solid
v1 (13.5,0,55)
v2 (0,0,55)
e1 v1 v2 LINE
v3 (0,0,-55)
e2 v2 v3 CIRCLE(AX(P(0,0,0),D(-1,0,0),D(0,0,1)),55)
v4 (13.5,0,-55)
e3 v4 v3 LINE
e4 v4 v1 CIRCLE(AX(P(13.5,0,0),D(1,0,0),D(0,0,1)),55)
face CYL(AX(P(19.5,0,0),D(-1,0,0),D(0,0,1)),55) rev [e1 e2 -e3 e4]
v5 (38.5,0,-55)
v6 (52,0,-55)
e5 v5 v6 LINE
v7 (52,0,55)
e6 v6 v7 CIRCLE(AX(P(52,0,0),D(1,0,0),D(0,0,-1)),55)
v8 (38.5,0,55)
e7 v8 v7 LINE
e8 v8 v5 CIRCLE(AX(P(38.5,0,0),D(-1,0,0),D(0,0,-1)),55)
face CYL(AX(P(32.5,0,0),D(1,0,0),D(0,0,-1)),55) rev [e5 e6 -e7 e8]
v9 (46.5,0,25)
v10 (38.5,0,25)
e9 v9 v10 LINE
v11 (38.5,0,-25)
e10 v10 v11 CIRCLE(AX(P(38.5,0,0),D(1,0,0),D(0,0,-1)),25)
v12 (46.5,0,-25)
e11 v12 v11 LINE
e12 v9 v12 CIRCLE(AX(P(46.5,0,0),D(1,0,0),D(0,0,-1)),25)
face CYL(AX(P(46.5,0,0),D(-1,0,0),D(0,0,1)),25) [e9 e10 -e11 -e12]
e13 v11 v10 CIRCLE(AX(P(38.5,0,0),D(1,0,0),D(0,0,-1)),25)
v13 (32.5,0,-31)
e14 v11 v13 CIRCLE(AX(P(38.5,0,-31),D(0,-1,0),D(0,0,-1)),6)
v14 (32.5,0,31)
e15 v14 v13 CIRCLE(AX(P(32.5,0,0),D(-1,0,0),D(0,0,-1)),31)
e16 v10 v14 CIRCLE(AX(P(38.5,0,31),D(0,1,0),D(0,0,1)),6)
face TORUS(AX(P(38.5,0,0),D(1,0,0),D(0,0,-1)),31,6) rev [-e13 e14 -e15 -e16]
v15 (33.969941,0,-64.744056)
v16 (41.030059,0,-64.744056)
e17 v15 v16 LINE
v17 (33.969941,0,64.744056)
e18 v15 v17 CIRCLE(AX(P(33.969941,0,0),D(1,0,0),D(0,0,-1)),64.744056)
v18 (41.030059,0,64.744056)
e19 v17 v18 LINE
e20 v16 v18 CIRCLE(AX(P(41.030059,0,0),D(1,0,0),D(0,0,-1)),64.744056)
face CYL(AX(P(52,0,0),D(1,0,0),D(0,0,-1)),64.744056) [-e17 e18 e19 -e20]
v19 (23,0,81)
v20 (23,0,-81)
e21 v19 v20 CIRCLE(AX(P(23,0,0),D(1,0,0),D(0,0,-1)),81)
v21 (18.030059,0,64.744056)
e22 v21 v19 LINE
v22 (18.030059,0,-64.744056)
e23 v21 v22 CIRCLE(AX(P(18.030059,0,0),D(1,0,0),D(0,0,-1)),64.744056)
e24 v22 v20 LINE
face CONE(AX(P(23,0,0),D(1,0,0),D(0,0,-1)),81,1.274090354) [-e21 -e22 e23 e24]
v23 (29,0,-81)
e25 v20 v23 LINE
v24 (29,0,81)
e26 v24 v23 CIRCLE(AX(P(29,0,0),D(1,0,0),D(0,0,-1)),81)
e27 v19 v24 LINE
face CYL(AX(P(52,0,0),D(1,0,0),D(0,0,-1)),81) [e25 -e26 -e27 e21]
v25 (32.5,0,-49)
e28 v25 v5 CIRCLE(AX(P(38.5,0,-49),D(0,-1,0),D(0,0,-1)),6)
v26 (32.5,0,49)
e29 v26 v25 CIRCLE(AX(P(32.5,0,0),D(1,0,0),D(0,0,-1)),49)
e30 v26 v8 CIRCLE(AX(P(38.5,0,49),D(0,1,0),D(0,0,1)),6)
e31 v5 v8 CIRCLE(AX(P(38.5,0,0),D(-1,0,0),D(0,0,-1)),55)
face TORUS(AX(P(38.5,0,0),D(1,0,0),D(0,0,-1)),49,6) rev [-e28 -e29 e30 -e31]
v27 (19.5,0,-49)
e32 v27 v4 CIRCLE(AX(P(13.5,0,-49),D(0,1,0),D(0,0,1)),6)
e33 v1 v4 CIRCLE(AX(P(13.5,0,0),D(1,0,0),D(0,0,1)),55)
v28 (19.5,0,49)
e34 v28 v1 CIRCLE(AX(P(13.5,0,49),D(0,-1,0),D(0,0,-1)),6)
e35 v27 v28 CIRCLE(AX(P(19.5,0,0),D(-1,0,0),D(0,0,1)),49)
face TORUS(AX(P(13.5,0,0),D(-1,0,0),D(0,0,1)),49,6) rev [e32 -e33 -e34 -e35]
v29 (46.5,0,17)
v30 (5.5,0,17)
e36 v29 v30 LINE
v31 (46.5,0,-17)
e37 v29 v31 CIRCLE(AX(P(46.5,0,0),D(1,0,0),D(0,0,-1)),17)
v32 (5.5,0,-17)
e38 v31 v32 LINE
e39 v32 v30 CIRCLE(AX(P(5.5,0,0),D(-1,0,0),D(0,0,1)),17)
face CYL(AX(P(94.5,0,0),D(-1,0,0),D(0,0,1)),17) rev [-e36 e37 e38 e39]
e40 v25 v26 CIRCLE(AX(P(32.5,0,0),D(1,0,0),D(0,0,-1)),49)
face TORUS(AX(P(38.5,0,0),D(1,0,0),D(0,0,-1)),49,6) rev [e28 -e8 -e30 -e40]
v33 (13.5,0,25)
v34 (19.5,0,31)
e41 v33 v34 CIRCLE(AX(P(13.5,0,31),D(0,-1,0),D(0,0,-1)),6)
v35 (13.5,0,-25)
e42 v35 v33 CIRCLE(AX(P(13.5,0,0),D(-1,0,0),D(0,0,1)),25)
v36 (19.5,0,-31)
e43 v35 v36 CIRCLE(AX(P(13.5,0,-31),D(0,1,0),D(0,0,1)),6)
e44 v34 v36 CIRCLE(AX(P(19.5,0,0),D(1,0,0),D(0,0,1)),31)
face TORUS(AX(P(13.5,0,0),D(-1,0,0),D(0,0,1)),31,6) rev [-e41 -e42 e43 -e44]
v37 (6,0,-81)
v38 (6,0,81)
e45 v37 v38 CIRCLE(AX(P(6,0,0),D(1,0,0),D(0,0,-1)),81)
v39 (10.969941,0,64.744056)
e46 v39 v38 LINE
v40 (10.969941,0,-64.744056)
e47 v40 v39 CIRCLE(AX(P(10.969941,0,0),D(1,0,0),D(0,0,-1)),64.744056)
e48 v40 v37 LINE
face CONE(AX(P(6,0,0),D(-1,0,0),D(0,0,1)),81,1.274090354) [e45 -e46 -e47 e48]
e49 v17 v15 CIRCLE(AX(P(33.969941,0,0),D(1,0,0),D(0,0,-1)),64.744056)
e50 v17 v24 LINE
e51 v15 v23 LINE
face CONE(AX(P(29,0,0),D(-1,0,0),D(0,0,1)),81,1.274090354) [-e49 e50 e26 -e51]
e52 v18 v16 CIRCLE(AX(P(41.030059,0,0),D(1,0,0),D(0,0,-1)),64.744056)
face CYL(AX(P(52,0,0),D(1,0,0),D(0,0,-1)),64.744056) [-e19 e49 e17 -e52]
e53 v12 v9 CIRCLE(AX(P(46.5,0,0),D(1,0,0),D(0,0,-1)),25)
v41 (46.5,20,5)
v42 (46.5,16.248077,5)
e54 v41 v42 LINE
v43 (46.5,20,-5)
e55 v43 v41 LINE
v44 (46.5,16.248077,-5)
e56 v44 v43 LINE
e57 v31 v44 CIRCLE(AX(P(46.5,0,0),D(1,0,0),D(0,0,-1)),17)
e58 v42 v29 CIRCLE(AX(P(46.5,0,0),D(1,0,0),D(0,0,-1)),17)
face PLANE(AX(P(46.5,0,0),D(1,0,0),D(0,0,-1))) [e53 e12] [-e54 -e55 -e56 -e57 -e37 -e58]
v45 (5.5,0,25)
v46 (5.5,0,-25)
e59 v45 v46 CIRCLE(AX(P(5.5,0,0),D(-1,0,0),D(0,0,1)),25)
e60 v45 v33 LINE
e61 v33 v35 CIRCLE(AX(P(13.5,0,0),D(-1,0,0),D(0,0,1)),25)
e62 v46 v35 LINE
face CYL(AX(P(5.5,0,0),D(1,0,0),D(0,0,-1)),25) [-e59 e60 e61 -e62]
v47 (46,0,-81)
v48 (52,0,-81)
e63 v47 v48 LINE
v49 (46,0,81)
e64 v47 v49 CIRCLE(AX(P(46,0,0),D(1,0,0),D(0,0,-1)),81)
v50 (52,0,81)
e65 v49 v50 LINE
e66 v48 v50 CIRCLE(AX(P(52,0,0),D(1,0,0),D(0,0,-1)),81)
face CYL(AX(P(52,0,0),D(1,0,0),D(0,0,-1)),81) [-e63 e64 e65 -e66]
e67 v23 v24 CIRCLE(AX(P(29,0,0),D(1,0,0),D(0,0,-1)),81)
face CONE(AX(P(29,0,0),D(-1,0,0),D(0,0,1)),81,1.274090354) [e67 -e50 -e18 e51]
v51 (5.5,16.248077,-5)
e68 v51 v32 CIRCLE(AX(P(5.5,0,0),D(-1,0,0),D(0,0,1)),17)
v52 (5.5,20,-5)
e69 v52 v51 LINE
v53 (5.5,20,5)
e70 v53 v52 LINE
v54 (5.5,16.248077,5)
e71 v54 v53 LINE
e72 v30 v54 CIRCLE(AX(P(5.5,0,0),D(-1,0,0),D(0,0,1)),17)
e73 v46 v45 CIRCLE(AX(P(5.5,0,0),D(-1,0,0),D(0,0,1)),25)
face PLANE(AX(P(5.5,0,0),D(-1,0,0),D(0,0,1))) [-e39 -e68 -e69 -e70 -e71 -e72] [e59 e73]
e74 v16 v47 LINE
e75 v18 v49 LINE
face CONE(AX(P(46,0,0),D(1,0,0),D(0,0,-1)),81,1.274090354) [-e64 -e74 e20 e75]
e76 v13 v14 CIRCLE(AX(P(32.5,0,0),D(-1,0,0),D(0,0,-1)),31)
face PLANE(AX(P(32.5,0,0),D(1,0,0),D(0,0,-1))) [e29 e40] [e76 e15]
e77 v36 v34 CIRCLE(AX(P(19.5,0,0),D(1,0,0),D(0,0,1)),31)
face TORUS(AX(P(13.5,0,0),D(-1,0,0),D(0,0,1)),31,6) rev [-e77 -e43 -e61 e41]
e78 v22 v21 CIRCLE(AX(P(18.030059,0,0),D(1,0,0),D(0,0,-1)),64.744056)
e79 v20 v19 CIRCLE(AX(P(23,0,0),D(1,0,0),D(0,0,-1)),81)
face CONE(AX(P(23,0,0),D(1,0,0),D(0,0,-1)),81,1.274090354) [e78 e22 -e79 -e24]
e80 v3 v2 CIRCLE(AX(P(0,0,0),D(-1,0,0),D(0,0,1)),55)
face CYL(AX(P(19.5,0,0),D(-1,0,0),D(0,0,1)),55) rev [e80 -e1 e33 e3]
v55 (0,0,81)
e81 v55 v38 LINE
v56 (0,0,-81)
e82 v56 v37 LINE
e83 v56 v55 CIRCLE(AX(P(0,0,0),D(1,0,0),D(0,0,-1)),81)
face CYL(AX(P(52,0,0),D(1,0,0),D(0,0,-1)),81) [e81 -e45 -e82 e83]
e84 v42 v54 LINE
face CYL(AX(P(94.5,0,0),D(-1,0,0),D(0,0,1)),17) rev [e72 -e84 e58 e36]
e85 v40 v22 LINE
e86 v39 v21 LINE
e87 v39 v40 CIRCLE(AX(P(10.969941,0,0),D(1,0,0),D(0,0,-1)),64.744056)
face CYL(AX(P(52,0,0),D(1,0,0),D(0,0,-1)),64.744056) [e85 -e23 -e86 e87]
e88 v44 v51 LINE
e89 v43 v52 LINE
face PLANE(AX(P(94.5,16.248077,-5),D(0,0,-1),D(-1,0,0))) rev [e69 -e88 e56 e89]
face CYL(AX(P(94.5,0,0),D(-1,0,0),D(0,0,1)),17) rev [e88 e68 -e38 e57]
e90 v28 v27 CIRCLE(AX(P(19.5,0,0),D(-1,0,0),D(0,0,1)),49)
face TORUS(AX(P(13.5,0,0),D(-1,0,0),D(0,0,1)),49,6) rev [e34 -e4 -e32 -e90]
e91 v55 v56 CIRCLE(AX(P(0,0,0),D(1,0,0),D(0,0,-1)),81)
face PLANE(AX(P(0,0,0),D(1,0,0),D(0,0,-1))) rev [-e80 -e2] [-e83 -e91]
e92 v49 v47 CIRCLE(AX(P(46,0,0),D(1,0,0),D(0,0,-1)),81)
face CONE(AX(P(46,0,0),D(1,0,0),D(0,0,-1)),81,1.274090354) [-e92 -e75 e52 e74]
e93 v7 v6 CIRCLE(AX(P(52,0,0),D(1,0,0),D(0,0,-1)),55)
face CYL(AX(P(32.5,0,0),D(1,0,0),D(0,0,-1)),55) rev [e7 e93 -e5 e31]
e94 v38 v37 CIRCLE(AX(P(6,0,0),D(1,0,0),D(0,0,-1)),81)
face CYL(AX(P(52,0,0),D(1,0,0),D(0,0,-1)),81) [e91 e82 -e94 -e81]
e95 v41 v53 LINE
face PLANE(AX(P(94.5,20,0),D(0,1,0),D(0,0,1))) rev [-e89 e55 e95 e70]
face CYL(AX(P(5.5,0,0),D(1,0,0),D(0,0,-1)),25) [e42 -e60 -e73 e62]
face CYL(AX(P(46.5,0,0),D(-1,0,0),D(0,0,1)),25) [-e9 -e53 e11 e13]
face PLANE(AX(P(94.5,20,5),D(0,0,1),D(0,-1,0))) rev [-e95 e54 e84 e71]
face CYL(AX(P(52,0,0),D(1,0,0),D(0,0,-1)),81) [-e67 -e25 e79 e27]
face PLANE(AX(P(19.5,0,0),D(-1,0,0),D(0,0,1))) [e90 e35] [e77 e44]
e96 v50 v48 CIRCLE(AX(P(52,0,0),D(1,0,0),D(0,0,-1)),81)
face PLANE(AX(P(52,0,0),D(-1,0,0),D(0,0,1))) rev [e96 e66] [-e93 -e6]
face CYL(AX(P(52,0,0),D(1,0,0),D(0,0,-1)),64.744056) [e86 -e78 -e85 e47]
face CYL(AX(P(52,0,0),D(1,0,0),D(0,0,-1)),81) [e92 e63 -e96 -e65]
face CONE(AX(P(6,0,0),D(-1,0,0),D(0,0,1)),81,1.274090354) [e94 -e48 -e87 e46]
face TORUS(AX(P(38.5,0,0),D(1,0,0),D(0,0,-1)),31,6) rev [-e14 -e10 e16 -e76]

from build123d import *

# Parameters (mm, degrees)
FRONT_RECESS_110_SKETCH_R    = 55
FRONT_RECESS_110_DEPTH       = 19.5
REAR_START                   = -19.5
REAR_RECESS_110_SKETCH_R     = 55
REAR_RECESS_110_DEPTH        = 19.5
FRONT_HUB_50_SKETCH_R        = 25
FRONT_HUB_50_DEPTH           = 14
REAR_START_2                 = 14
REAR_HUB_50_SKETCH_R         = 25
REAR_HUB_50_DEPTH            = 14
KEYED_BORE_20_DEPTH          = 89
FRONT_RECESS_RIM_FILLET_R6_R = 6
REAR_RECESS_RIM_FILLET_R6_R  = 6
FRONT_HUB_ROOT_FILLET_R6_R   = 6
REAR_HUB_ROOT_FILLET_R6_R    = 6


with BuildPart() as part:
    # Pulley Rim Profile Sketch → Twin Groove Pulley Body (revolve)
    with BuildSketch(Plane.XY, mode=Mode.PRIVATE) as twin_groove_pulley_body_sk:
        Polygon((52, 0), (0, 0), (0, 81), (6, 81), (10.969940868, 64.744055898), (18.030059132, 64.744055898), (23, 81), (29, 81), (33.969940868, 64.744055898), (41.030059132, 64.744055898), (46, 81), (52, 81), align=None)
    revolve(twin_groove_pulley_body_sk.sketch.rotate(Axis((52, 0, 0), (-1, 0, 0)), 90), axis=Axis((52, 0, 0), (-1, 0, 0)))

    # Front Recess Ø110 Sketch → Front Recess Ø110 (cut)
    with BuildSketch(Plane(origin=(52, 0, 0), x_dir=(0, 0, -1), z_dir=(1, 0, 0))):
        Circle(FRONT_RECESS_110_SKETCH_R)
    extrude(amount=-FRONT_RECESS_110_DEPTH, mode=Mode.SUBTRACT)

    # Rear Recess Ø110 Sketch → Rear Recess Ø110 (cut)
    with BuildSketch(Plane.ZY.offset(REAR_START)):
        with Locations(Location((0, 0, 0), (0, 0, 180))):
            Circle(REAR_RECESS_110_SKETCH_R)
    extrude(amount=REAR_RECESS_110_DEPTH, mode=Mode.SUBTRACT)

    # Front Hub Ø50 Sketch → Front Hub Ø50 (add)
    with BuildSketch(Plane(origin=(32.5, 0, 0), x_dir=(0, 0, -1), z_dir=(1, 0, 0))):
        Circle(FRONT_HUB_50_SKETCH_R)
    extrude(amount=FRONT_HUB_50_DEPTH)

    # Rear Hub Ø50 Sketch → Rear Hub Ø50 (add)
    with BuildSketch(Plane.ZY.offset(-19.5).offset(REAR_START_2)):
        with Locations(Location((0, 0, 0), (0, 0, 180))):
            Circle(REAR_HUB_50_SKETCH_R)
    extrude(amount=-REAR_HUB_50_DEPTH)

    # Keyed Bore Ø20 Sketch → Keyed Bore Ø20 (cut)
    with BuildSketch(Plane.ZY.offset(-5.5)):
        with BuildLine():
            Line((0, 20), (5, 20))
            Line((5, 20), (5, 16.248076809))
            ThreePointArc((5, 16.248076809), (0, -17), (-5, 16.248076809))
            Line((-5, 16.248076809), (-5, 20))
            Line((-5, 20), (0, 20))
        make_face()
    extrude(amount=-KEYED_BORE_20_DEPTH, mode=Mode.SUBTRACT)

    # Front Recess Rim Fillet R6
    front_recess_rim_fillet_r6_edges = [part.edges().sort_by_distance(p)[0] for p in [
        (32.5, 0, 55),
    ]]
    fillet(front_recess_rim_fillet_r6_edges, radius=FRONT_RECESS_RIM_FILLET_R6_R)

    # Rear Recess Rim Fillet R6
    rear_recess_rim_fillet_r6_edges = [part.edges().sort_by_distance(p)[0] for p in [
        (19.5, 0, 55),
    ]]
    fillet(rear_recess_rim_fillet_r6_edges, radius=REAR_RECESS_RIM_FILLET_R6_R)

    # Front Hub Root Fillet R6
    front_hub_root_fillet_r6_edges = [part.edges().sort_by_distance(p)[0] for p in [
        (32.5, 0, 25),
    ]]
    fillet(front_hub_root_fillet_r6_edges, radius=FRONT_HUB_ROOT_FILLET_R6_R)

    # Rear Hub Root Fillet R6
    rear_hub_root_fillet_r6_edges = [part.edges().sort_by_distance(p)[0] for p in [
        (19.5, 0, 25),
    ]]
    fillet(rear_hub_root_fillet_r6_edges, radius=REAR_HUB_ROOT_FILLET_R6_R)


solid = part.part
